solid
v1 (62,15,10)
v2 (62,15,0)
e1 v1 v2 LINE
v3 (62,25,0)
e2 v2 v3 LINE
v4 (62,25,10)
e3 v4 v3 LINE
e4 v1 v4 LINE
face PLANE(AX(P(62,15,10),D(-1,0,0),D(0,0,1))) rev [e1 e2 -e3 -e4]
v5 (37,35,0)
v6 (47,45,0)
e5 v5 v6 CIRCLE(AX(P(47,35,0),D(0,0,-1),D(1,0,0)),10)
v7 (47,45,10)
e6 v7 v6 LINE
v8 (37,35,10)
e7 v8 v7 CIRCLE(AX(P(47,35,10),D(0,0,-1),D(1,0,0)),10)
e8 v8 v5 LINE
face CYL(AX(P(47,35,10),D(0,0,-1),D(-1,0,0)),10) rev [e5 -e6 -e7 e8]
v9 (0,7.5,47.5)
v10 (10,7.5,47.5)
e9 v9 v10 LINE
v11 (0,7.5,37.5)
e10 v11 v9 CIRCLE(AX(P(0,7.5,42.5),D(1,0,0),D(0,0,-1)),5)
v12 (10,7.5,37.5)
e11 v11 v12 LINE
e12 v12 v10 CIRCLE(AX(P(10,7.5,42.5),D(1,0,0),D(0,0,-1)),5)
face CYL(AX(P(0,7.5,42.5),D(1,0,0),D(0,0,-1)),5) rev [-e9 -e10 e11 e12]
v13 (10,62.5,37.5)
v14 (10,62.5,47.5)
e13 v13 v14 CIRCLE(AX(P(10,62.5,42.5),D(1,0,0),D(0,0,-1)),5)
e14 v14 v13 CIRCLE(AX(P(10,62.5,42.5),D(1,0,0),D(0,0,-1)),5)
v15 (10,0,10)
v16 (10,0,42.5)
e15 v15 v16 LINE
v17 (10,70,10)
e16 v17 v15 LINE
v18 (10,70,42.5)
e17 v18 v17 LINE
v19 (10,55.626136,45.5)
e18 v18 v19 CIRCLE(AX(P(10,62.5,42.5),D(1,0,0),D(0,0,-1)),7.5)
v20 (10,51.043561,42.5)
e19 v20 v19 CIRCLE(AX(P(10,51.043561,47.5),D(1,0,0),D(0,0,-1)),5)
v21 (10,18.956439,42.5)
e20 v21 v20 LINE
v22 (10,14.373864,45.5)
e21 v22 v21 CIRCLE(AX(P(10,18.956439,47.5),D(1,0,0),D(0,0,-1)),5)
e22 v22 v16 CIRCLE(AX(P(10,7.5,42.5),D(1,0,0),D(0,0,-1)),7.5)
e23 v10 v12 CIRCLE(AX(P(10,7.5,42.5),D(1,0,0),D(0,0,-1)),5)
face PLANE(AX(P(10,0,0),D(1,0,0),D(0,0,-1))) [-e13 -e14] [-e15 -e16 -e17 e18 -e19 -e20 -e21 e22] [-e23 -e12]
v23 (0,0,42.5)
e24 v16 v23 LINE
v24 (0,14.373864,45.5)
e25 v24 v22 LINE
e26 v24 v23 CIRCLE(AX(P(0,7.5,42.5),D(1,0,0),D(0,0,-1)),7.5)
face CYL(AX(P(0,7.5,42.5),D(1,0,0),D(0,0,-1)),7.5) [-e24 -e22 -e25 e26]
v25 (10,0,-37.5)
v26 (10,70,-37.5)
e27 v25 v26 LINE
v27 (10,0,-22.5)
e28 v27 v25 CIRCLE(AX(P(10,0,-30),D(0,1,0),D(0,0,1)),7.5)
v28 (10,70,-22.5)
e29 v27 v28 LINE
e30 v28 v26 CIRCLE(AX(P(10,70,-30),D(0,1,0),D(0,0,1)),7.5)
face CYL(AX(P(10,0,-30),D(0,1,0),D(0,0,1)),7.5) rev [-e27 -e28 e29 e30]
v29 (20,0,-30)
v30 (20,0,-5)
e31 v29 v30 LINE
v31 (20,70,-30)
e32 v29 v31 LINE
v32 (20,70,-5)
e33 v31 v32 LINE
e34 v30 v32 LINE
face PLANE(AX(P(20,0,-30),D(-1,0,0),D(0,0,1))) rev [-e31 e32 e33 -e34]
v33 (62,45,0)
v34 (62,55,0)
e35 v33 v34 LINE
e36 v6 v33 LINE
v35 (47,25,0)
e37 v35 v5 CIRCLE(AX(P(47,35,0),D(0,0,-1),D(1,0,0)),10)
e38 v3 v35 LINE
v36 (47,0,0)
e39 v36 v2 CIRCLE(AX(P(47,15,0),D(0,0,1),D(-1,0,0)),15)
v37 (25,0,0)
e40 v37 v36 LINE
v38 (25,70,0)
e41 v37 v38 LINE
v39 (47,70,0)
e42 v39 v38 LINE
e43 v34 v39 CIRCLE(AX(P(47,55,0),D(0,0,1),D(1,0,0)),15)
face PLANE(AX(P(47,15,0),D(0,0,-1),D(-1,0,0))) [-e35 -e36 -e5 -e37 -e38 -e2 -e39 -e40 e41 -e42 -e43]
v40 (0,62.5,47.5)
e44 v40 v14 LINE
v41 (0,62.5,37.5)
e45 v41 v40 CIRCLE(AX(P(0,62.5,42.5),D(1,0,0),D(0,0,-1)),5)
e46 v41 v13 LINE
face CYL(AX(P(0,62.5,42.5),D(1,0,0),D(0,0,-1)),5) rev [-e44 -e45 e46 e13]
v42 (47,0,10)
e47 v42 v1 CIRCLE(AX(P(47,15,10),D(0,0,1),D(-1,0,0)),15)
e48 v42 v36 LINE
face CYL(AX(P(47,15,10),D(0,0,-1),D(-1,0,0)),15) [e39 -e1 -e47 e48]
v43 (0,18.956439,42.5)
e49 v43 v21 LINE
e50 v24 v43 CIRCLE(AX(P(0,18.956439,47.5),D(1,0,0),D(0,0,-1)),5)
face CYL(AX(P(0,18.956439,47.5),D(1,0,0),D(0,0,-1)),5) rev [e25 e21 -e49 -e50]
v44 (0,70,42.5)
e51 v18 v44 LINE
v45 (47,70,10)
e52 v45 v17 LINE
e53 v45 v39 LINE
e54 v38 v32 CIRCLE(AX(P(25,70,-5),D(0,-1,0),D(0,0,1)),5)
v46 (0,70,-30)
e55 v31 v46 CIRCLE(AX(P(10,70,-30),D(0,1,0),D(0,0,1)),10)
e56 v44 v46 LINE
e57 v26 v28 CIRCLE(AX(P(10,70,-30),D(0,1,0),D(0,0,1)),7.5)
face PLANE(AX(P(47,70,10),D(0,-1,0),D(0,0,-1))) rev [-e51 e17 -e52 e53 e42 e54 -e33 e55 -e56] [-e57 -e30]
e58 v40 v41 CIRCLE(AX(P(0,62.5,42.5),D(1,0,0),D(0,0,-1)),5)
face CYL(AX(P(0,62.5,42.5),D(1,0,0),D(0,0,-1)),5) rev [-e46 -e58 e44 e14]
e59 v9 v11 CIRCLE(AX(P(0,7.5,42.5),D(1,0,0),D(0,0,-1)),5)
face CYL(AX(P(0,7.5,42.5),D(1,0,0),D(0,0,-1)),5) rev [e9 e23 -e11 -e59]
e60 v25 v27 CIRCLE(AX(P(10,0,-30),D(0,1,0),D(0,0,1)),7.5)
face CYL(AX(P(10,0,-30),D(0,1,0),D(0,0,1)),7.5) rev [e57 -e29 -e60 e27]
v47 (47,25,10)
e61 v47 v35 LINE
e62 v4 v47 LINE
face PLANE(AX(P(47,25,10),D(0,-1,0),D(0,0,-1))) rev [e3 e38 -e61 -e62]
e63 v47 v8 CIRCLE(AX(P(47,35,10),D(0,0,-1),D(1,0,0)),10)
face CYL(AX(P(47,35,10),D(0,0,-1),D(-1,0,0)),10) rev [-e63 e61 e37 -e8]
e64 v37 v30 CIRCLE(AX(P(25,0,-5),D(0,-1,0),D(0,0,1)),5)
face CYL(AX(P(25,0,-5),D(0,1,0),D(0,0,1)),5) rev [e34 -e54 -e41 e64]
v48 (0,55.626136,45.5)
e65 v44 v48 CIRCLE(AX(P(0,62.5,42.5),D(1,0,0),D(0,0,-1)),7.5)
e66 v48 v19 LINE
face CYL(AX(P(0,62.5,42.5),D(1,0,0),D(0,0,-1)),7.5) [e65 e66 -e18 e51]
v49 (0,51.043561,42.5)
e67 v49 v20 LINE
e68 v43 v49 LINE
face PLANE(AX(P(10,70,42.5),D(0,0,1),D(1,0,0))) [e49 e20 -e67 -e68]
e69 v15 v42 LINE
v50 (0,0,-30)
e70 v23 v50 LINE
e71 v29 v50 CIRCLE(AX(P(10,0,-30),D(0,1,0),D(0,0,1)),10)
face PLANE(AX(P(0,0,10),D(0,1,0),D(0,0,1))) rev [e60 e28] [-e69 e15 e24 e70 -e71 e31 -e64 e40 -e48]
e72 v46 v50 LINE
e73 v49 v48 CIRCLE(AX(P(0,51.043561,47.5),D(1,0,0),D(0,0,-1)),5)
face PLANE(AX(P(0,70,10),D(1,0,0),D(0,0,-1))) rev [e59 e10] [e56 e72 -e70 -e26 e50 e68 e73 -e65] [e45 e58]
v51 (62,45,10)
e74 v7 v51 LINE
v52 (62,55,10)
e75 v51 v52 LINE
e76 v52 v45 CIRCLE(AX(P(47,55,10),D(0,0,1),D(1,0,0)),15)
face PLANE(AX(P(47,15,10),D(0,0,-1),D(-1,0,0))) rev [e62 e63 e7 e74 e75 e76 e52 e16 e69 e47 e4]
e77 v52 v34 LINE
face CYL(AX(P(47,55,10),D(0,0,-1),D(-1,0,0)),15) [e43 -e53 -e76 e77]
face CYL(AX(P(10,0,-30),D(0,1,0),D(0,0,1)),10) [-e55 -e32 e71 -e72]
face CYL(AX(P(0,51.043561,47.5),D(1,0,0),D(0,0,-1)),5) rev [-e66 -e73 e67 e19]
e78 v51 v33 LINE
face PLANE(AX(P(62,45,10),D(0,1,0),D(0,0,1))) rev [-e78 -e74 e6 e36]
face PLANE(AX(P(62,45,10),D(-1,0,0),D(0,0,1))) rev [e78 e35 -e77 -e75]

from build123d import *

# Parameters (mm, degrees)
BASE_PLATE_DEPTH         = 10
MOUNTING_FLANGE_SKETCH_W = 32.5
MOUNTING_FLANGE_SKETCH_H = 70
MOUNTING_FLANGE_DEPTH    = 10
FLANGE_LUGS_DEPTH        = 10
MOUNTING_HOLE_SKETCH_R   = 5
MOUNTING_HOLES_DEPTH     = 10
UPRIGHT_WEB_SKETCH_W     = 30
UPRIGHT_WEB_SKETCH_H     = 70
UPRIGHT_WEB_DEPTH        = 25
WEB_RELIEF_CUT_SKETCH_W  = 5
WEB_RELIEF_CUT_SKETCH_H  = 30
WEB_RELIEF_CUT_DEPTH     = 70
ROUNDED_ARM_DEPTH        = 70
BORE_BOSS_DEPTH          = 70
BORE_SKETCH_R            = 7.5
THROUGH_BORE_DEPTH       = 70


with BuildPart() as part:
    # Base Plate Sketch → Base Plate (new body)
    with BuildSketch(Plane.XY):
        with BuildLine():
            Line((0, 0), (47, 0))
            ThreePointArc((47, 0), (57.606601718, 4.393398282), (62, 15))
            Line((62, 15), (62, 25))
            Line((62, 25), (47, 25))
            ThreePointArc((47, 25), (37, 35), (47, 45))
            Line((47, 45), (62, 45))
            Line((62, 45), (62, 55))
            ThreePointArc((62, 55), (57.606601718, 65.606601718), (47, 70))
            Line((47, 70), (0, 70))
            Line((0, 70), (0, 0))
        make_face()
    extrude(amount=BASE_PLATE_DEPTH)

    # Mounting Flange Sketch → Mounting Flange (add)
    with BuildSketch(Plane.ZY):
        with Locations((26.25, 35)):
            Rectangle(MOUNTING_FLANGE_SKETCH_W, MOUNTING_FLANGE_SKETCH_H)
    extrude(amount=-MOUNTING_FLANGE_DEPTH)

    # Flange Lug Sketch → Flange Lugs (add)
    with BuildSketch(Plane(origin=(10, 0, 0), x_dir=(0, 0, -1), z_dir=(1, 0, 0))):
        with BuildLine():
            ThreePointArc((-45.5, 55.626136458), (-43.316699867, 53.78217355), (-42.5, 51.043560763))
            Line((-42.5, 51.043560763), (-42.5, 70))
            ThreePointArc((-42.5, 70), (-49.841797347, 64.032322328), (-45.5, 55.626136458))
        make_face()
        with BuildLine():
            Line((-42.5, 0), (-42.5, 18.956439237))
            ThreePointArc((-42.5, 18.956439237), (-43.316699867, 16.21782645), (-45.5, 14.373863542))
            ThreePointArc((-45.5, 14.373863542), (-49.841797347, 5.967677672), (-42.5, 0))
        make_face()
    extrude(amount=-FLANGE_LUGS_DEPTH)

    # Mounting Hole Sketch → Mounting Holes (cut)
    with BuildSketch(Plane(origin=(10, 0, 0), x_dir=(0, 0, -1), z_dir=(1, 0, 0))):
        with Locations((-42.5, 62.5)):
            Circle(MOUNTING_HOLE_SKETCH_R)
        with Locations((-42.5, 7.5)):
            Circle(MOUNTING_HOLE_SKETCH_R)
    extrude(amount=-MOUNTING_HOLES_DEPTH, mode=Mode.SUBTRACT)

    # Upright Web Sketch → Upright Web (add)
    with BuildSketch(Plane.ZY):
        with Locations((-15, 35)):
            Rectangle(UPRIGHT_WEB_SKETCH_W, UPRIGHT_WEB_SKETCH_H)
    extrude(amount=-UPRIGHT_WEB_DEPTH)

    # Web Relief Cut Sketch → Web Relief Cut (cut)
    with BuildSketch(Plane(origin=(0, 70, 0), x_dir=(1, 0, 0), z_dir=(0, 1, 0))):
        with Locations((22.5, 15)):
            Rectangle(WEB_RELIEF_CUT_SKETCH_W, WEB_RELIEF_CUT_SKETCH_H)
    extrude(amount=-WEB_RELIEF_CUT_DEPTH, mode=Mode.SUBTRACT)

    # Rounded Arm Sketch → Rounded Arm (add)
    with BuildSketch(Plane(origin=(0, 70, 0), x_dir=(1, 0, 0), z_dir=(0, 1, 0))):
        with BuildLine():
            Line((20, 0), (25, 0))
            ThreePointArc((25, 0), (21.464466094, 1.464466094), (20, 5))
            Line((20, 5), (20, 0))
        make_face()
    extrude(amount=-ROUNDED_ARM_DEPTH)

    # Bore Boss Sketch → Bore Boss (add)
    with BuildSketch(Plane(origin=(0, 70, 0), x_dir=(1, 0, 0), z_dir=(0, 1, 0))):
        with BuildLine():
            Line((0, 30), (20, 30))
            ThreePointArc((20, 30), (10, 40), (0, 30))
        make_face()
    extrude(amount=-BORE_BOSS_DEPTH)

    # Bore Sketch → Through Bore (cut)
    with BuildSketch(Plane(origin=(0, 70, 0), x_dir=(1, 0, 0), z_dir=(0, 1, 0))):
        with Locations(Location((10, 30, 0), (0, 0, 270))):
            Circle(BORE_SKETCH_R)
    extrude(amount=-THROUGH_BORE_DEPTH, mode=Mode.SUBTRACT)


solid = part.part
